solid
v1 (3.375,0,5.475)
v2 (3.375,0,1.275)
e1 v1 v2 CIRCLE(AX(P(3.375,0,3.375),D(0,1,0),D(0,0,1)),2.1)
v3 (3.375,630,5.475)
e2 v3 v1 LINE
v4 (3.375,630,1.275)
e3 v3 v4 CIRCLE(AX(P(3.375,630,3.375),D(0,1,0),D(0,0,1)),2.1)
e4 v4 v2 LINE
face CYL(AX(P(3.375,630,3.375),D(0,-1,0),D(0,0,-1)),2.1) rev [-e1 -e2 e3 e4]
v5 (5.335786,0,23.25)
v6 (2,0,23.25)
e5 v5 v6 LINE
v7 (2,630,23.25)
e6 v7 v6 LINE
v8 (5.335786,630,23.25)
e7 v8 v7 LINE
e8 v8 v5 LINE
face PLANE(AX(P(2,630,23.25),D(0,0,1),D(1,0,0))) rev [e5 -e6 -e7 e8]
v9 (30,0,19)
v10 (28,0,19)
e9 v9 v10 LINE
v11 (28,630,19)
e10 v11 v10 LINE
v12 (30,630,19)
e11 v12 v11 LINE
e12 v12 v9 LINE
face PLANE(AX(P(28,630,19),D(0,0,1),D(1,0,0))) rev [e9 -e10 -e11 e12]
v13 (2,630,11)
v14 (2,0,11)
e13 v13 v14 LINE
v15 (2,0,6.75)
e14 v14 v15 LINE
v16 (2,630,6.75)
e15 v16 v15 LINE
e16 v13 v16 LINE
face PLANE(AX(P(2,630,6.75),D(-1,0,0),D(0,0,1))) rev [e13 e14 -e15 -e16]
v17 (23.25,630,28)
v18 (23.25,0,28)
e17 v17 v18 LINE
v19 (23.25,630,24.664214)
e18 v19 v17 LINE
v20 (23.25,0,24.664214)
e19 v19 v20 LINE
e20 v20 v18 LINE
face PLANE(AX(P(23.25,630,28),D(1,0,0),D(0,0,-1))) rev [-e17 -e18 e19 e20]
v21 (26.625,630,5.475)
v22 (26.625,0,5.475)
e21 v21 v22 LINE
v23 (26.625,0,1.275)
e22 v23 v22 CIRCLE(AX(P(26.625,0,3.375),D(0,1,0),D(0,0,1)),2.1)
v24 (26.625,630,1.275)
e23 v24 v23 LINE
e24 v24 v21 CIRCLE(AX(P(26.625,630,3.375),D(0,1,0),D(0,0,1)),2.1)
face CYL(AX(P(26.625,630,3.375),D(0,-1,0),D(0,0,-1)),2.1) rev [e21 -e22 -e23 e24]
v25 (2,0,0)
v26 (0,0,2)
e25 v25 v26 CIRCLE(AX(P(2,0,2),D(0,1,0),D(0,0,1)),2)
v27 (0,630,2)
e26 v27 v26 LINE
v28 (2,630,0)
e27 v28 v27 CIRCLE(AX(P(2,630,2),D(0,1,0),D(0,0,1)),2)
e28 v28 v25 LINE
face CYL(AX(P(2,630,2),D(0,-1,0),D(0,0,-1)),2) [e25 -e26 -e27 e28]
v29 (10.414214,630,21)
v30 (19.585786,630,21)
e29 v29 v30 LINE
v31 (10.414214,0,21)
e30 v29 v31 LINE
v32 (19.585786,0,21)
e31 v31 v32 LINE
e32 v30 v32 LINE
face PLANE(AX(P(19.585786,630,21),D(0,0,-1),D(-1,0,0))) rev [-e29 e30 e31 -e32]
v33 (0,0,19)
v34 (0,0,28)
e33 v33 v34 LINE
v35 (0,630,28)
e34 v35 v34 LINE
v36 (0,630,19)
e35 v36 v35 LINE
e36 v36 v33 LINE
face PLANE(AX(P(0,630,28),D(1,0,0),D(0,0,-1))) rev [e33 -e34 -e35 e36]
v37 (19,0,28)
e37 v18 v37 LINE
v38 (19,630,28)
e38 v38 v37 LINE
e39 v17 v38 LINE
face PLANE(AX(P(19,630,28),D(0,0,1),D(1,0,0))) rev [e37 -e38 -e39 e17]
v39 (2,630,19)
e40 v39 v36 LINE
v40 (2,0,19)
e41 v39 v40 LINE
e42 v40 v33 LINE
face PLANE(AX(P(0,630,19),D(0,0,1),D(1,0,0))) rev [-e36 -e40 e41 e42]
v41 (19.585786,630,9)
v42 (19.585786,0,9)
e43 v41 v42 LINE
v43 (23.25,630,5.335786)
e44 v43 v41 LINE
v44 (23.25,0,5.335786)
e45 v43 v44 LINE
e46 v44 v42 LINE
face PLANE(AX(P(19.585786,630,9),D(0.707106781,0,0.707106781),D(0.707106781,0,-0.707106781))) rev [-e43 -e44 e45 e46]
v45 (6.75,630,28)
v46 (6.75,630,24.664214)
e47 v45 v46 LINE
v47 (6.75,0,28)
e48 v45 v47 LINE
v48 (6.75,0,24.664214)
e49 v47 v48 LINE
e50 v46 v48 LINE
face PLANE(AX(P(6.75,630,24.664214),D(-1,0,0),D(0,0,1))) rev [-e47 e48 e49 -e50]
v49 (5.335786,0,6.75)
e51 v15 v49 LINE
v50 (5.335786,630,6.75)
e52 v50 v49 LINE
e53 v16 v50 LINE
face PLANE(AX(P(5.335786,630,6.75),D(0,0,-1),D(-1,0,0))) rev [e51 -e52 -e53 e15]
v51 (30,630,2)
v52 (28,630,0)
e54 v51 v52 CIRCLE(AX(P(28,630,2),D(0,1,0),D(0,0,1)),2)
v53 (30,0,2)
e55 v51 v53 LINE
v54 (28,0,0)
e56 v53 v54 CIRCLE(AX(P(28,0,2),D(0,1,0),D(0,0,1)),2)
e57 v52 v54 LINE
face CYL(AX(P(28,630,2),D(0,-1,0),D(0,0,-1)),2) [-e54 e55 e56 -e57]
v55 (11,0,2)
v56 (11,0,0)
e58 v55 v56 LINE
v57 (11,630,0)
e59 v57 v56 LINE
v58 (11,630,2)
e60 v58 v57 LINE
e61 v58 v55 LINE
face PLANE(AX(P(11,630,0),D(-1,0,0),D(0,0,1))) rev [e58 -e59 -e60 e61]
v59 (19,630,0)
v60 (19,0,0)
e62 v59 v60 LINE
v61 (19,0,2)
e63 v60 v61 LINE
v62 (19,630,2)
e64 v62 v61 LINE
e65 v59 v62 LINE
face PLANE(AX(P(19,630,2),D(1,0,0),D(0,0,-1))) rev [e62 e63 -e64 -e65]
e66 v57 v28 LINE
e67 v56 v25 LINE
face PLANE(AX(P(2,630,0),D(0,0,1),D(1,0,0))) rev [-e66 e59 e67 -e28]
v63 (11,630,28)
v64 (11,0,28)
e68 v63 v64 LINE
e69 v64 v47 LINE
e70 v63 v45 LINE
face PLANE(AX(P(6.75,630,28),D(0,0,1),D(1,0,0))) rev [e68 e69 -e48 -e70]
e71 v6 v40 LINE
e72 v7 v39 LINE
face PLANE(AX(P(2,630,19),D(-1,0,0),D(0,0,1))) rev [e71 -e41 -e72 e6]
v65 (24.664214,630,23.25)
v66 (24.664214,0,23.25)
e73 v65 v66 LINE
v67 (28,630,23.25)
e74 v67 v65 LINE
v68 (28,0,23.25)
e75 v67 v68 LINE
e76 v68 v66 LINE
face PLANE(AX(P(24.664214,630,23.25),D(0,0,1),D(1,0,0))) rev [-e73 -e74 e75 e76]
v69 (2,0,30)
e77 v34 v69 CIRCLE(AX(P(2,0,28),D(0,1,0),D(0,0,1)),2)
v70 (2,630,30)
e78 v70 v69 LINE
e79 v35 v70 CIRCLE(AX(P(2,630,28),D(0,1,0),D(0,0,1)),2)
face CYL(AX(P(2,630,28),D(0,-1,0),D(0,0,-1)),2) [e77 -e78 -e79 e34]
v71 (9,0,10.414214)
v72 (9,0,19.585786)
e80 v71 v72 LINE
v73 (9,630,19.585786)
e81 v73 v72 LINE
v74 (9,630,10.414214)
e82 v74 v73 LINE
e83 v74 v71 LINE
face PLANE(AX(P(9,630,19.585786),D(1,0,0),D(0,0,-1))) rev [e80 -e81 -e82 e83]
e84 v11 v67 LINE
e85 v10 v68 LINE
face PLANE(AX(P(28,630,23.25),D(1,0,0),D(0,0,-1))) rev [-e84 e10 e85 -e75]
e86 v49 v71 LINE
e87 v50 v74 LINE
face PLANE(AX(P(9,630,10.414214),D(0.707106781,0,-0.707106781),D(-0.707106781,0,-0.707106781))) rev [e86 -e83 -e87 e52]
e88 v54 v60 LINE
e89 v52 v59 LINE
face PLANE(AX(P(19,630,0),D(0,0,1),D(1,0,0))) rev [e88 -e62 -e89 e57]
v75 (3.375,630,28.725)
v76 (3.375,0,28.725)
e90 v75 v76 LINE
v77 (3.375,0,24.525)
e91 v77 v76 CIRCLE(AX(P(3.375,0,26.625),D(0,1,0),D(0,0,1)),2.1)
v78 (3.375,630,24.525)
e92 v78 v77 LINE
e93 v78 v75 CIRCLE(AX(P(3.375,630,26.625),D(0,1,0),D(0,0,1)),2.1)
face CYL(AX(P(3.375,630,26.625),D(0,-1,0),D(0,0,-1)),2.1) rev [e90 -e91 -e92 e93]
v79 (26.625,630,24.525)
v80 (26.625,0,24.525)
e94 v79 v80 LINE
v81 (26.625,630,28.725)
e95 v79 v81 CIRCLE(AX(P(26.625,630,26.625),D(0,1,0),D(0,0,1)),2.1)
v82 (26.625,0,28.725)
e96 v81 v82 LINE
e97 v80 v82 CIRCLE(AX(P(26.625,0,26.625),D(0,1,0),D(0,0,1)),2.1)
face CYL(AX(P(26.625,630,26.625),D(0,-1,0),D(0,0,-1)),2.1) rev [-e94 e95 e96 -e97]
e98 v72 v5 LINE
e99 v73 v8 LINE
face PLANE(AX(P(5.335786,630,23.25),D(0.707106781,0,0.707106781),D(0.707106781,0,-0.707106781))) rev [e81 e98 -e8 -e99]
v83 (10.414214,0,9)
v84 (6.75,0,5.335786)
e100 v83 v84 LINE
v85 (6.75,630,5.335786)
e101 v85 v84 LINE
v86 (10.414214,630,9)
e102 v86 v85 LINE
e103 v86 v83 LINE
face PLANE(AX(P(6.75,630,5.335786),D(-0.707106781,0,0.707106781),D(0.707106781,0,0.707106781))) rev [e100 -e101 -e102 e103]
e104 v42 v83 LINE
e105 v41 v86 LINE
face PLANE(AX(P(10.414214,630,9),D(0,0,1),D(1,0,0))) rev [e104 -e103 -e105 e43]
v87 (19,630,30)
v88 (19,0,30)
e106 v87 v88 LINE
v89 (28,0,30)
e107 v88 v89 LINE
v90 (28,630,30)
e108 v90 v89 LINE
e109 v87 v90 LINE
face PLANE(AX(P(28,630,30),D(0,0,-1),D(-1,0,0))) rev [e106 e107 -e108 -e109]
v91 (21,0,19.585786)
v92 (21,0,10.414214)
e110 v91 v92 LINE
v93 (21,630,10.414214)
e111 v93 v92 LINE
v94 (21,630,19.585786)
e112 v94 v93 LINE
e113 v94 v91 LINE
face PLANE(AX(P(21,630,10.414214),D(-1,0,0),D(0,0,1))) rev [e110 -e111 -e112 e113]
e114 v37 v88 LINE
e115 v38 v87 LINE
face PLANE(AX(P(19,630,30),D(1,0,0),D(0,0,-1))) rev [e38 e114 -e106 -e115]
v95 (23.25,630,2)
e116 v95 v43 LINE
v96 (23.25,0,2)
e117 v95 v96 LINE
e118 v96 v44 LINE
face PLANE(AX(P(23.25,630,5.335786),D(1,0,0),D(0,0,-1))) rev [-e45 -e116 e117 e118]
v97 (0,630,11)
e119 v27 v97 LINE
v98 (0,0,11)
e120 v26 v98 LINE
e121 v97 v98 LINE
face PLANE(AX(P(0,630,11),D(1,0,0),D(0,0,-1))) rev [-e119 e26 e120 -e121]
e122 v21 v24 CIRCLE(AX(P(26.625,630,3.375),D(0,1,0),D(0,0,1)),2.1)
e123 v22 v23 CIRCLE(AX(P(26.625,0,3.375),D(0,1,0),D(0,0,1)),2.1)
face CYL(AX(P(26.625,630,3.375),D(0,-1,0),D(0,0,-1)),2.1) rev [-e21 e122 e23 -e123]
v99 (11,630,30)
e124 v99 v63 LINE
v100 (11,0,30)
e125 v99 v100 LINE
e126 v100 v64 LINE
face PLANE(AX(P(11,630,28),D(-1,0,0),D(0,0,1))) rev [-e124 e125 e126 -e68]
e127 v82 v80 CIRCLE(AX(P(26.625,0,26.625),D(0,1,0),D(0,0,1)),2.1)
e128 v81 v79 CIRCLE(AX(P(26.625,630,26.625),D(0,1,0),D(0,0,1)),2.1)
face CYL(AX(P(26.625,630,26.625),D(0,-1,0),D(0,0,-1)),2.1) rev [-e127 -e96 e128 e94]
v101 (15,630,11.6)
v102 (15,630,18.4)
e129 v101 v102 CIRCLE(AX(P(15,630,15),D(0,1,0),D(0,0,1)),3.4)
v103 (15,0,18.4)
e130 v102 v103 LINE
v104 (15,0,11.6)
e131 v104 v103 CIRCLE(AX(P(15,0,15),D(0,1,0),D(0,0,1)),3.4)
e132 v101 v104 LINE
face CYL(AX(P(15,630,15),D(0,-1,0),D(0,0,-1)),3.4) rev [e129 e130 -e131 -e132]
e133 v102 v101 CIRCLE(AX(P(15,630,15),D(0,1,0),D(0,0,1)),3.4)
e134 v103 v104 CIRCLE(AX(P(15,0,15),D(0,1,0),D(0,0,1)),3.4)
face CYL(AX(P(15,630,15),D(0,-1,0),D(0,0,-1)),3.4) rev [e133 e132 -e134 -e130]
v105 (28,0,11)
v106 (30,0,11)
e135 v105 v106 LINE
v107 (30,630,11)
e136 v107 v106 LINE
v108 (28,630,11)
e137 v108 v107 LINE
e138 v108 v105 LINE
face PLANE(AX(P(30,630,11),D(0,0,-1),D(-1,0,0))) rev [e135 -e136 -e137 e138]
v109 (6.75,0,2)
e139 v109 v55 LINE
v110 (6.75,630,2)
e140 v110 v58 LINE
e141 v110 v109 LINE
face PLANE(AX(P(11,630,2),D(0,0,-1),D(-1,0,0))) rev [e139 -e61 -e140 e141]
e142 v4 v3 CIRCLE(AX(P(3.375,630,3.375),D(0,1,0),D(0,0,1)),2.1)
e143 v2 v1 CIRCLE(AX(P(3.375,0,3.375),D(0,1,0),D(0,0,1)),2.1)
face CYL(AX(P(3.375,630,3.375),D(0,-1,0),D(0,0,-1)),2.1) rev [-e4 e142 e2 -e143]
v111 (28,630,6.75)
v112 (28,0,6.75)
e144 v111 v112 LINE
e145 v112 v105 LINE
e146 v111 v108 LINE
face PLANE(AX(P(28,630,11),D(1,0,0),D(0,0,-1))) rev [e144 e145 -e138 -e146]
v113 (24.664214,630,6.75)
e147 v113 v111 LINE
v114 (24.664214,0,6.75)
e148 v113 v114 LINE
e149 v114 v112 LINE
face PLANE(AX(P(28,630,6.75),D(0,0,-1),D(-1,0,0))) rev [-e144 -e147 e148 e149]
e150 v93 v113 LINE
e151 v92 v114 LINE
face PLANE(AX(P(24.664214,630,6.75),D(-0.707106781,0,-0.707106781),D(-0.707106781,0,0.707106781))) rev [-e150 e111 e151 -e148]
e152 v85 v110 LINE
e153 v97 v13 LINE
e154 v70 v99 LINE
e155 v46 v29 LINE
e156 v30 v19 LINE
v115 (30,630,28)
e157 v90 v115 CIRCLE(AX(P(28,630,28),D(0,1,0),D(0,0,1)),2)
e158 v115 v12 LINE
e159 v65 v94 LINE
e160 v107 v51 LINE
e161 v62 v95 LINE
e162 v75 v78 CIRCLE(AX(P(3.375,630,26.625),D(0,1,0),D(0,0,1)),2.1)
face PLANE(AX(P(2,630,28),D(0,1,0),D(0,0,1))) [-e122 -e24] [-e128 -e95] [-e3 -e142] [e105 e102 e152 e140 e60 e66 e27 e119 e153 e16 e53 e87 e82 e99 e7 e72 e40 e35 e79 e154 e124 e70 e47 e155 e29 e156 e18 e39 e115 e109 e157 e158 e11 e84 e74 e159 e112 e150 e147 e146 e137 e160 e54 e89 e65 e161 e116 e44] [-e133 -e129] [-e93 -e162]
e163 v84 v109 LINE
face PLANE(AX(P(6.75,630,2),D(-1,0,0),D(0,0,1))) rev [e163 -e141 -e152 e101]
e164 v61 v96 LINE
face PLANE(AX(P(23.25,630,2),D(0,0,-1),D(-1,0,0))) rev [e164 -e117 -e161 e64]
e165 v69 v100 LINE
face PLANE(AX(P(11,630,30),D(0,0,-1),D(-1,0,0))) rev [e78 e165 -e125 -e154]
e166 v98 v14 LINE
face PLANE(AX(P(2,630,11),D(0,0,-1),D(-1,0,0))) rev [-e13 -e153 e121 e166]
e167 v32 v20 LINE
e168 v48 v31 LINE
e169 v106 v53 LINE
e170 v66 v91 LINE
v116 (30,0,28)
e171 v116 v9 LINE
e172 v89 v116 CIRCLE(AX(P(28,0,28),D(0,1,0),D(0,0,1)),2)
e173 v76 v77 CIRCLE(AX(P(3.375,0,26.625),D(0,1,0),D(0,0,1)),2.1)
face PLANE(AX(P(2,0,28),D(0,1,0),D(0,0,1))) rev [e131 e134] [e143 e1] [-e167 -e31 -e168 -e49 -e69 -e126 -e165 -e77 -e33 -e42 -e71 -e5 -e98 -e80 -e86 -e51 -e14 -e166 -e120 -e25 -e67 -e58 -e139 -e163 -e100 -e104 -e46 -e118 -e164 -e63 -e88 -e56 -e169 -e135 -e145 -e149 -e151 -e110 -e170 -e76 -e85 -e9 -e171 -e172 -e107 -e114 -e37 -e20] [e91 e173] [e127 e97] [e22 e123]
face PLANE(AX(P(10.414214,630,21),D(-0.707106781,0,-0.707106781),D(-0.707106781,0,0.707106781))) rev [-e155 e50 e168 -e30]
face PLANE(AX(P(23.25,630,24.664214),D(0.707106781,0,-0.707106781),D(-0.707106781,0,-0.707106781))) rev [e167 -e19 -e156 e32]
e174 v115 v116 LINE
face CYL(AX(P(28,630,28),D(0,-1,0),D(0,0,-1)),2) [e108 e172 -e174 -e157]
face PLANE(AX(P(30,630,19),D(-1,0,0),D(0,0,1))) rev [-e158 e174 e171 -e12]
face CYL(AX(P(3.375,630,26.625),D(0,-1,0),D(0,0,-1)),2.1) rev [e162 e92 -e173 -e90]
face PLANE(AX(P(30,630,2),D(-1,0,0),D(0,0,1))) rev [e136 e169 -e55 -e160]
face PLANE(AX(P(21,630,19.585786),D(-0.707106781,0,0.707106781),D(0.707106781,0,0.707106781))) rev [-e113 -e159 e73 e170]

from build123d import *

# Parameters (mm, degrees)
SKETCH_1_R      = 2.1
SKETCH_1_R_2    = 3.4
EXTRUDE_1_DEPTH = 630


with BuildPart() as part:
    # 草图1 → 拉伸1 (new body)
    with BuildSketch(Plane(origin=(0, 0, 0), x_dir=(1, 0, 0), z_dir=(0, 1, 0))):
        with BuildLine():
            Line((6.75, -28), (11, -28))
            Line((11, -28), (11, -30))
            Line((11, -30), (2, -30))
            ThreePointArc((2, -30), (0.585786438, -29.414213562), (0, -28))
            Line((0, -28), (0, -19))
            Line((0, -19), (2, -19))
            Line((2, -19), (2, -23.25))
            Line((2, -23.25), (5.335785999, -23.25))
            Line((5.335785999, -23.25), (9, -19.585785999))
            Line((9, -19.585785999), (9, -10.414214001))
            Line((9, -10.414214001), (5.335785999, -6.75))
            Line((5.335785999, -6.75), (2, -6.75))
            Line((2, -6.75), (2, -11))
            Line((2, -11), (0, -11))
            Line((0, -11), (0, -2))
            ThreePointArc((0, -2), (0.585786438, -0.585786438), (2, 0))
            Line((2, 0), (11, 0))
            Line((11, 0), (11, -2))
            Line((11, -2), (6.75, -2))
            Line((6.75, -2), (6.75, -5.335785999))
            Line((6.75, -5.335785999), (10.414214001, -9))
            Line((10.414214001, -9), (19.585785999, -9))
            Line((19.585785999, -9), (23.25, -5.335785999))
            Line((23.25, -5.335785999), (23.25, -2))
            Line((23.25, -2), (19, -2))
            Line((19, -2), (19, 0))
            Line((19, 0), (28, 0))
            ThreePointArc((28, 0), (29.414213562, -0.585786438), (30, -2))
            Line((30, -2), (30, -11))
            Line((30, -11), (28, -11))
            Line((28, -11), (28, -6.75))
            Line((28, -6.75), (24.664214001, -6.75))
            Line((24.664214001, -6.75), (21, -10.414214001))
            Line((21, -10.414214001), (21, -19.585785999))
            Line((21, -19.585785999), (24.664214001, -23.25))
            Line((24.664214001, -23.25), (28, -23.25))
            Line((28, -23.25), (28, -19))
            Line((28, -19), (30, -19))
            Line((30, -19), (30, -28))
            ThreePointArc((30, -28), (29.414213562, -29.414213562), (28, -30))
            Line((28, -30), (19, -30))
            Line((19, -30), (19, -28))
            Line((19, -28), (23.25, -28))
            Line((23.25, -28), (23.25, -24.664214001))
            Line((23.25, -24.664214001), (19.585785999, -21))
            Line((19.585785999, -21), (10.414214001, -21))
            Line((10.414214001, -21), (6.75, -24.664214001))
            Line((6.75, -24.664214001), (6.75, -28))
        make_face()
        with Locations(Location((3.375, -26.625, 0), (0, 0, 270))):
            Circle(SKETCH_1_R, mode=Mode.SUBTRACT)
        with Locations(Location((26.625, -26.625, 0), (0, 0, 270))):
            Circle(SKETCH_1_R, mode=Mode.SUBTRACT)
        with Locations(Location((15, -15, 0), (0, 0, 270))):
            Circle(SKETCH_1_R_2, mode=Mode.SUBTRACT)
        with Locations(Location((3.375, -3.375, 0), (0, 0, 270))):
            Circle(SKETCH_1_R, mode=Mode.SUBTRACT)
        with Locations(Location((26.625, -3.375, 0), (0, 0, 270))):
            Circle(SKETCH_1_R, mode=Mode.SUBTRACT)
    extrude(amount=EXTRUDE_1_DEPTH)


solid = part.part
